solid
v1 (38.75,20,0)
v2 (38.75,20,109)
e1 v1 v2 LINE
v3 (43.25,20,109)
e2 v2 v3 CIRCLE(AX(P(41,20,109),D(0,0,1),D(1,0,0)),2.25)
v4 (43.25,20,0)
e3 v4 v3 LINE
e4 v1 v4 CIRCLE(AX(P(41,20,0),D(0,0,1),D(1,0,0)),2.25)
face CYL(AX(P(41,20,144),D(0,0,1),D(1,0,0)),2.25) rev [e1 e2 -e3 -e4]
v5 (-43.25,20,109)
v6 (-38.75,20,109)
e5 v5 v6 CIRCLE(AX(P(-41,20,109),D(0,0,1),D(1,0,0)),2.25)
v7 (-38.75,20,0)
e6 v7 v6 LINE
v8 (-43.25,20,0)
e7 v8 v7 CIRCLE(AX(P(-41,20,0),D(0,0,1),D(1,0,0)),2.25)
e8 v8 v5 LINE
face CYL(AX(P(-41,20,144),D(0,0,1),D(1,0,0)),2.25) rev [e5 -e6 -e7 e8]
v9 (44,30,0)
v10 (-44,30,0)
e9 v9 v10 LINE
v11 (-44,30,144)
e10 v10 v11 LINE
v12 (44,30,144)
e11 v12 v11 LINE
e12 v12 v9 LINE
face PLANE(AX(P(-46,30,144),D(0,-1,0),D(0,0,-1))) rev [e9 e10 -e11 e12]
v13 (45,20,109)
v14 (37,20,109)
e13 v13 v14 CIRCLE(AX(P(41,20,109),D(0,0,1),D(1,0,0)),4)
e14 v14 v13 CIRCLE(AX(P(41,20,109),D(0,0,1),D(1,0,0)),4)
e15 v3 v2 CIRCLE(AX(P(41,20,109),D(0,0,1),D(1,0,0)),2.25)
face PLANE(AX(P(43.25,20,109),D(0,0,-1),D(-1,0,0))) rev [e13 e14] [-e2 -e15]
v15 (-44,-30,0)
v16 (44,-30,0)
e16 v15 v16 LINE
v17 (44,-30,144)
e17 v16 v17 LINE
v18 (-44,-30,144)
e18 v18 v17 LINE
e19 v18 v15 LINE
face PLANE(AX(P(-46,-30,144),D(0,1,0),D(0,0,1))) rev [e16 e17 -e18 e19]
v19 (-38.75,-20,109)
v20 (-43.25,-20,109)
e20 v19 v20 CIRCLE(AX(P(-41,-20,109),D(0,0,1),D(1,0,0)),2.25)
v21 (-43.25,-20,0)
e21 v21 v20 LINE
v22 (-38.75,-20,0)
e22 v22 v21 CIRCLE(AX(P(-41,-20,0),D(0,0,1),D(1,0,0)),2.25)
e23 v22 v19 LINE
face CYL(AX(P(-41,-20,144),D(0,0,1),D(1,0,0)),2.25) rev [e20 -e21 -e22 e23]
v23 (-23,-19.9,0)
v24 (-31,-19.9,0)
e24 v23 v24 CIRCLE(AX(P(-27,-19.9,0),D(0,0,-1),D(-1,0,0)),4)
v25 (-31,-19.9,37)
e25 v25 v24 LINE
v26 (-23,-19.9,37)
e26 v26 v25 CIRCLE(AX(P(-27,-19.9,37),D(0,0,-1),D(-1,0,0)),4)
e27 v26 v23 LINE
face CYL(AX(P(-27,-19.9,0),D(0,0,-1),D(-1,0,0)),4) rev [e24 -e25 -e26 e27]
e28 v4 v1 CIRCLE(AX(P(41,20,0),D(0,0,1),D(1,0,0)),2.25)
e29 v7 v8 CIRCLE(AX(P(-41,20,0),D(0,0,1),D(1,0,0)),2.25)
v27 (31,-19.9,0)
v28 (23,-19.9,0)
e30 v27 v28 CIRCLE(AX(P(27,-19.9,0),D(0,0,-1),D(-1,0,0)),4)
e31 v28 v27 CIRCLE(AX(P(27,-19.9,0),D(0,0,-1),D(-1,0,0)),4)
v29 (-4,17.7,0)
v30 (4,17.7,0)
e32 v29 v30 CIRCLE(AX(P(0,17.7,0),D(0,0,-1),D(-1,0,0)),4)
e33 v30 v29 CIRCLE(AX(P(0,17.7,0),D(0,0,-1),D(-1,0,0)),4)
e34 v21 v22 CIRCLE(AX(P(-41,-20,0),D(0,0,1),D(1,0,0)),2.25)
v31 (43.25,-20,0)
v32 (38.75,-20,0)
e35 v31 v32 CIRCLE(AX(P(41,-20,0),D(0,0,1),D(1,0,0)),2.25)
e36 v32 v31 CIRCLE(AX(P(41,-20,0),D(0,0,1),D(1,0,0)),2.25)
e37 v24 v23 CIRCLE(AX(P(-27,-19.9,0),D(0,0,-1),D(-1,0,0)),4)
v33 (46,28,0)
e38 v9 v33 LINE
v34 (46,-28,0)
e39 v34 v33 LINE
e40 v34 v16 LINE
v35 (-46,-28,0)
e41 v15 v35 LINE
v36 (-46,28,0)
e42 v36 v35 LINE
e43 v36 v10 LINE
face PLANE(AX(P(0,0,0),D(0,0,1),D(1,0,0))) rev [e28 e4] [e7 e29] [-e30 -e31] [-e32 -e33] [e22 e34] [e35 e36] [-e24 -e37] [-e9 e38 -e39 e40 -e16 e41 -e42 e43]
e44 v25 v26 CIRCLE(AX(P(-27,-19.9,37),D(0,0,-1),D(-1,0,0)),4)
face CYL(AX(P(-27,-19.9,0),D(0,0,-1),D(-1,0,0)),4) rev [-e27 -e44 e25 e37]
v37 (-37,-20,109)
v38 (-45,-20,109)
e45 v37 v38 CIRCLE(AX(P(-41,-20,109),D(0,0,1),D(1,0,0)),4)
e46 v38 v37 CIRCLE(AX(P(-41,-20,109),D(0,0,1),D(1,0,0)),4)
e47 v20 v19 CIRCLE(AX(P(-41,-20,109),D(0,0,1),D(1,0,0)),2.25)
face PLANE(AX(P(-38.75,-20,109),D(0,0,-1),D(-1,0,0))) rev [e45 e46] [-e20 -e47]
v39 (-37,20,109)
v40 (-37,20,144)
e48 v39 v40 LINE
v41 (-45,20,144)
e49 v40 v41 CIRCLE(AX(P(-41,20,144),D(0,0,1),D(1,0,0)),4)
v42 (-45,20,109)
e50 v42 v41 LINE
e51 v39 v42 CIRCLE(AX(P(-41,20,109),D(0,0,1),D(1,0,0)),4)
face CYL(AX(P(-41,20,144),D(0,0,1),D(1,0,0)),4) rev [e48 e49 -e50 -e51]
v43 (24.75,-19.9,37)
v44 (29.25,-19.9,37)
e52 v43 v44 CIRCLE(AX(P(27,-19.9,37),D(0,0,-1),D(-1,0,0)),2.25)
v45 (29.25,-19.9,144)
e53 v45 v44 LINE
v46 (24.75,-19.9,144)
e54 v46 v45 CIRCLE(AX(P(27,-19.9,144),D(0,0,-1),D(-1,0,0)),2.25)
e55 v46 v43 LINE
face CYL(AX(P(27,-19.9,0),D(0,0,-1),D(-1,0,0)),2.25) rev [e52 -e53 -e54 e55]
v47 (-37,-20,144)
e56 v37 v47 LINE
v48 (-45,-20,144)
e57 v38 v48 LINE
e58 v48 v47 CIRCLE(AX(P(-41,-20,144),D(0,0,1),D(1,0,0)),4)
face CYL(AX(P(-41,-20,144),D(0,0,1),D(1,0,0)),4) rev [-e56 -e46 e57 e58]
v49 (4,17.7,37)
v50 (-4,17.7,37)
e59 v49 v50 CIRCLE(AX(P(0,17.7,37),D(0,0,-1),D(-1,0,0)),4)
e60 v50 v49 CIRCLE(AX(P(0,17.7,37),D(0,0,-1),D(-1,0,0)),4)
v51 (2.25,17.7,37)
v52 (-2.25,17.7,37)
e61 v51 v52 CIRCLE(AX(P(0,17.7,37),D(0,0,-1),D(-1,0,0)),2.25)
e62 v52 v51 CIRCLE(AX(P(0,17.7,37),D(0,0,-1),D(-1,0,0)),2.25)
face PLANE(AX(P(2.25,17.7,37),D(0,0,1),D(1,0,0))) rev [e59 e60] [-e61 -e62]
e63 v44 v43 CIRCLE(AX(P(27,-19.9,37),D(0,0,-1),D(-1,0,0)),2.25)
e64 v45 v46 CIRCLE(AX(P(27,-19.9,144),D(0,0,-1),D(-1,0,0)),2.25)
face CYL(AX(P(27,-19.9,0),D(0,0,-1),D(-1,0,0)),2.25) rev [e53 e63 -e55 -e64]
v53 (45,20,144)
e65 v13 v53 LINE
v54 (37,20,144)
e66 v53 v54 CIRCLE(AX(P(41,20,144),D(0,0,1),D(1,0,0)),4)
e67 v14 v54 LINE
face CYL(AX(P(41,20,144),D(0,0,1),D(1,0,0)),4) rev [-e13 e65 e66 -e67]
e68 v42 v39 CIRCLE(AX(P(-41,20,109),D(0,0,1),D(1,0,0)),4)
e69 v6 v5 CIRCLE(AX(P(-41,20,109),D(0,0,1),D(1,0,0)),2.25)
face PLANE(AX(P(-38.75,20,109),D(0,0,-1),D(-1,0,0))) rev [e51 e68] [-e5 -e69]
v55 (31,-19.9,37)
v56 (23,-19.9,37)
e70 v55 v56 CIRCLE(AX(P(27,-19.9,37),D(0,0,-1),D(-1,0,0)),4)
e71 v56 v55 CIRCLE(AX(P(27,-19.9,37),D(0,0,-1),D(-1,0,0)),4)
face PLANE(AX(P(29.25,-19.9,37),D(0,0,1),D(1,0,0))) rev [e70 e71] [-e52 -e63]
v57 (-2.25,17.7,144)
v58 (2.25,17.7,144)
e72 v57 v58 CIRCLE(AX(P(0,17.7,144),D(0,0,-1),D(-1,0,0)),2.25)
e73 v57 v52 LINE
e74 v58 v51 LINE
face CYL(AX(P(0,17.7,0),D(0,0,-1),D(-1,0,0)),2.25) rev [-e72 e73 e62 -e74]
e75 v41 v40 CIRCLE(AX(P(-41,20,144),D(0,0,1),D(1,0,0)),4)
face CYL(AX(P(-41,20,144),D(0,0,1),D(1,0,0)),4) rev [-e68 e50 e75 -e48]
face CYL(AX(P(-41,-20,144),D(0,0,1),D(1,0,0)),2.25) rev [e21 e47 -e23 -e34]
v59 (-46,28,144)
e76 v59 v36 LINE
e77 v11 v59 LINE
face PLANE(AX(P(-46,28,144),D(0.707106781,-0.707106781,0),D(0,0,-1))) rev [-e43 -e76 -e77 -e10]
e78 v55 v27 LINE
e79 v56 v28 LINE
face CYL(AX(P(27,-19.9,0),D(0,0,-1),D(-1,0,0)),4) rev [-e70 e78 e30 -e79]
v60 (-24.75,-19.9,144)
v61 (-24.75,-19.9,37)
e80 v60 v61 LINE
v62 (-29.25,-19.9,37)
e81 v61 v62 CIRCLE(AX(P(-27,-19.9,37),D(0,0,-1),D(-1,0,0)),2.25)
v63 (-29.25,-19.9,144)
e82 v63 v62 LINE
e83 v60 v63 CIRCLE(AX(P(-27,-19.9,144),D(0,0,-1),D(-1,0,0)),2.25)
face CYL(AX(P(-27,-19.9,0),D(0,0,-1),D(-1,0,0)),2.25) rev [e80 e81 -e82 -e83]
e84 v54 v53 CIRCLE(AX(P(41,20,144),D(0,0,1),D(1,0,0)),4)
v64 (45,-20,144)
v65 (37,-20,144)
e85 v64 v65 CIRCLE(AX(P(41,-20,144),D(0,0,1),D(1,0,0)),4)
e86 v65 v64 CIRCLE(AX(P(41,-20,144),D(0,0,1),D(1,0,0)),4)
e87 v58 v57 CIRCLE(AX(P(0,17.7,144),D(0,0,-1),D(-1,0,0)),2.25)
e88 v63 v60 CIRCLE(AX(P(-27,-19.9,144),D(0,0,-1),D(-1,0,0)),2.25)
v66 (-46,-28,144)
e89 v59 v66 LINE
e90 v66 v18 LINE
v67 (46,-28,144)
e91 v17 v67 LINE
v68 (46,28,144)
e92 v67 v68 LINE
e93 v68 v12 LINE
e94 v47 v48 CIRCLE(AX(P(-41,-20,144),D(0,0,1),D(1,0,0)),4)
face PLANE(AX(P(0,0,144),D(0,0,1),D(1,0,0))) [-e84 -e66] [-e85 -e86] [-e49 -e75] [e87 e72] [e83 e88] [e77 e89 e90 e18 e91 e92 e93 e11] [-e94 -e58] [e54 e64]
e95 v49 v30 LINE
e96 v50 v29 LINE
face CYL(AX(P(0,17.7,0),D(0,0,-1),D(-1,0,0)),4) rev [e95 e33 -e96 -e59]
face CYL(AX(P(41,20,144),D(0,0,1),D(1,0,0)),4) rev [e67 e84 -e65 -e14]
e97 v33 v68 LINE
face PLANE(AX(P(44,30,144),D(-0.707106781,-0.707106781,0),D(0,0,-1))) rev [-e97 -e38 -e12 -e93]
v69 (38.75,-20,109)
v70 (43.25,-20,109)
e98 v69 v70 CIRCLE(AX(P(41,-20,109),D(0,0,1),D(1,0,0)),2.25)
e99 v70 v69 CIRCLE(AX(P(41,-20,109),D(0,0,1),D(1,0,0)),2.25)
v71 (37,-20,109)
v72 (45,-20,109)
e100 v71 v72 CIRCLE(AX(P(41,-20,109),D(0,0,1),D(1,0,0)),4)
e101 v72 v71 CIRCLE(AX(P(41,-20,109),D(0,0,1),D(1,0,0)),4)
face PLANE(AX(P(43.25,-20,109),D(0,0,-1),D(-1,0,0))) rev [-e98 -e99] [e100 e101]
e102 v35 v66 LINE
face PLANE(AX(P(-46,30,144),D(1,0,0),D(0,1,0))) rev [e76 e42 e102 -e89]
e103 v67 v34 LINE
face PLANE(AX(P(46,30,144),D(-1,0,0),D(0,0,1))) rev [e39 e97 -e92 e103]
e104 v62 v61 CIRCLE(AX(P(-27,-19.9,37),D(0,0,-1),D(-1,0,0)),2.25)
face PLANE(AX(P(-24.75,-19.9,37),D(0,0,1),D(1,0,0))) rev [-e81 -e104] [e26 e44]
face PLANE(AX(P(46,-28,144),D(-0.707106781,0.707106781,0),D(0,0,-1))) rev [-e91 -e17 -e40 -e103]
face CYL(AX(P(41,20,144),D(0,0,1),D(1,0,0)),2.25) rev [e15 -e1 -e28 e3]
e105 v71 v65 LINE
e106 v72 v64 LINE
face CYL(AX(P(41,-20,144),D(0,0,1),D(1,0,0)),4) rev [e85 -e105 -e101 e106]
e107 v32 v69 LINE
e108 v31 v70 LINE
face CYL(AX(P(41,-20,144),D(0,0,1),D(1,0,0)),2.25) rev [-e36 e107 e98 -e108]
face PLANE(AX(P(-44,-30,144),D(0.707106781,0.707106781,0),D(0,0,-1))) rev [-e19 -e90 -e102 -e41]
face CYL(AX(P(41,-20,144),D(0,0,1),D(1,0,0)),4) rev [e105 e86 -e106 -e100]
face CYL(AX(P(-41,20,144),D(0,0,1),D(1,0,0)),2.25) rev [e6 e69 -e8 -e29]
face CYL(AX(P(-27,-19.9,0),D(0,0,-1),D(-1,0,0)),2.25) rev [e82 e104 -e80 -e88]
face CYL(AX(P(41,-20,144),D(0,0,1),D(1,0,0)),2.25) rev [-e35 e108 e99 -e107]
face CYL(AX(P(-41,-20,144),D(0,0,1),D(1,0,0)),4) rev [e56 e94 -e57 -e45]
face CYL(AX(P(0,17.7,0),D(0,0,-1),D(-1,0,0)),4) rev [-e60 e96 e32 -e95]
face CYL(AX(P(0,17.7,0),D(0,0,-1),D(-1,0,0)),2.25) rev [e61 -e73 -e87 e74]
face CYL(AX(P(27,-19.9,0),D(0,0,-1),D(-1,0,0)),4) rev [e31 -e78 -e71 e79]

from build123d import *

# Parameters (mm, degrees)
SKETCH_1_W                   = 92
SKETCH_1_H                   = 60
EXTRUDE_1_DEPTH              = 144
HOLE_WIZARD_M4_1_D           = 4.5
HOLE_WIZARD_M4_1_CBORE_D     = 8
HOLE_WIZARD_M4_1_CBORE_DEPTH = 35
CHAMFER_1_SIZE               = 2
HOLE_WIZARD_M4_2_D           = 4.5
HOLE_WIZARD_M4_2_CBORE_D     = 8
HOLE_WIZARD_M4_2_CBORE_DEPTH = 37


with BuildPart() as part:
    # 草图1 → 凸台-拉伸1 (new body)
    with BuildSketch(Plane.XY):
        Rectangle(SKETCH_1_W, SKETCH_1_H)
    extrude(amount=EXTRUDE_1_DEPTH)

    # M4 六角凹头螺钉的柱形沉头孔1 (through all)
    with Locations(Plane.XY.offset(144)):
        with Locations((-41, 20), (-41, -20), (41, 20), (41, -20)):
            CounterBoreHole(HOLE_WIZARD_M4_1_D / 2, HOLE_WIZARD_M4_1_CBORE_D / 2, HOLE_WIZARD_M4_1_CBORE_DEPTH)

    # 倒角1
    chamfer_1_edges = [part.edges().sort_by_distance(p)[0] for p in [
        (46, -30, 72),
        (-46, -30, 72),
        (-46, 30, 72),
        (46, 30, 72),
    ]]
    chamfer(chamfer_1_edges, length=CHAMFER_1_SIZE)

    # M4 六角凹头螺钉的柱形沉头孔2 (through all)
    with Locations(Plane(origin=(0, 0, 0), x_dir=(-1, 0, 0), z_dir=(0, 0, -1))):
        with Locations((0, 17.7), (-27, -19.9), (27, -19.9)):
            CounterBoreHole(HOLE_WIZARD_M4_2_D / 2, HOLE_WIZARD_M4_2_CBORE_D / 2, HOLE_WIZARD_M4_2_CBORE_DEPTH)


solid = part.part
